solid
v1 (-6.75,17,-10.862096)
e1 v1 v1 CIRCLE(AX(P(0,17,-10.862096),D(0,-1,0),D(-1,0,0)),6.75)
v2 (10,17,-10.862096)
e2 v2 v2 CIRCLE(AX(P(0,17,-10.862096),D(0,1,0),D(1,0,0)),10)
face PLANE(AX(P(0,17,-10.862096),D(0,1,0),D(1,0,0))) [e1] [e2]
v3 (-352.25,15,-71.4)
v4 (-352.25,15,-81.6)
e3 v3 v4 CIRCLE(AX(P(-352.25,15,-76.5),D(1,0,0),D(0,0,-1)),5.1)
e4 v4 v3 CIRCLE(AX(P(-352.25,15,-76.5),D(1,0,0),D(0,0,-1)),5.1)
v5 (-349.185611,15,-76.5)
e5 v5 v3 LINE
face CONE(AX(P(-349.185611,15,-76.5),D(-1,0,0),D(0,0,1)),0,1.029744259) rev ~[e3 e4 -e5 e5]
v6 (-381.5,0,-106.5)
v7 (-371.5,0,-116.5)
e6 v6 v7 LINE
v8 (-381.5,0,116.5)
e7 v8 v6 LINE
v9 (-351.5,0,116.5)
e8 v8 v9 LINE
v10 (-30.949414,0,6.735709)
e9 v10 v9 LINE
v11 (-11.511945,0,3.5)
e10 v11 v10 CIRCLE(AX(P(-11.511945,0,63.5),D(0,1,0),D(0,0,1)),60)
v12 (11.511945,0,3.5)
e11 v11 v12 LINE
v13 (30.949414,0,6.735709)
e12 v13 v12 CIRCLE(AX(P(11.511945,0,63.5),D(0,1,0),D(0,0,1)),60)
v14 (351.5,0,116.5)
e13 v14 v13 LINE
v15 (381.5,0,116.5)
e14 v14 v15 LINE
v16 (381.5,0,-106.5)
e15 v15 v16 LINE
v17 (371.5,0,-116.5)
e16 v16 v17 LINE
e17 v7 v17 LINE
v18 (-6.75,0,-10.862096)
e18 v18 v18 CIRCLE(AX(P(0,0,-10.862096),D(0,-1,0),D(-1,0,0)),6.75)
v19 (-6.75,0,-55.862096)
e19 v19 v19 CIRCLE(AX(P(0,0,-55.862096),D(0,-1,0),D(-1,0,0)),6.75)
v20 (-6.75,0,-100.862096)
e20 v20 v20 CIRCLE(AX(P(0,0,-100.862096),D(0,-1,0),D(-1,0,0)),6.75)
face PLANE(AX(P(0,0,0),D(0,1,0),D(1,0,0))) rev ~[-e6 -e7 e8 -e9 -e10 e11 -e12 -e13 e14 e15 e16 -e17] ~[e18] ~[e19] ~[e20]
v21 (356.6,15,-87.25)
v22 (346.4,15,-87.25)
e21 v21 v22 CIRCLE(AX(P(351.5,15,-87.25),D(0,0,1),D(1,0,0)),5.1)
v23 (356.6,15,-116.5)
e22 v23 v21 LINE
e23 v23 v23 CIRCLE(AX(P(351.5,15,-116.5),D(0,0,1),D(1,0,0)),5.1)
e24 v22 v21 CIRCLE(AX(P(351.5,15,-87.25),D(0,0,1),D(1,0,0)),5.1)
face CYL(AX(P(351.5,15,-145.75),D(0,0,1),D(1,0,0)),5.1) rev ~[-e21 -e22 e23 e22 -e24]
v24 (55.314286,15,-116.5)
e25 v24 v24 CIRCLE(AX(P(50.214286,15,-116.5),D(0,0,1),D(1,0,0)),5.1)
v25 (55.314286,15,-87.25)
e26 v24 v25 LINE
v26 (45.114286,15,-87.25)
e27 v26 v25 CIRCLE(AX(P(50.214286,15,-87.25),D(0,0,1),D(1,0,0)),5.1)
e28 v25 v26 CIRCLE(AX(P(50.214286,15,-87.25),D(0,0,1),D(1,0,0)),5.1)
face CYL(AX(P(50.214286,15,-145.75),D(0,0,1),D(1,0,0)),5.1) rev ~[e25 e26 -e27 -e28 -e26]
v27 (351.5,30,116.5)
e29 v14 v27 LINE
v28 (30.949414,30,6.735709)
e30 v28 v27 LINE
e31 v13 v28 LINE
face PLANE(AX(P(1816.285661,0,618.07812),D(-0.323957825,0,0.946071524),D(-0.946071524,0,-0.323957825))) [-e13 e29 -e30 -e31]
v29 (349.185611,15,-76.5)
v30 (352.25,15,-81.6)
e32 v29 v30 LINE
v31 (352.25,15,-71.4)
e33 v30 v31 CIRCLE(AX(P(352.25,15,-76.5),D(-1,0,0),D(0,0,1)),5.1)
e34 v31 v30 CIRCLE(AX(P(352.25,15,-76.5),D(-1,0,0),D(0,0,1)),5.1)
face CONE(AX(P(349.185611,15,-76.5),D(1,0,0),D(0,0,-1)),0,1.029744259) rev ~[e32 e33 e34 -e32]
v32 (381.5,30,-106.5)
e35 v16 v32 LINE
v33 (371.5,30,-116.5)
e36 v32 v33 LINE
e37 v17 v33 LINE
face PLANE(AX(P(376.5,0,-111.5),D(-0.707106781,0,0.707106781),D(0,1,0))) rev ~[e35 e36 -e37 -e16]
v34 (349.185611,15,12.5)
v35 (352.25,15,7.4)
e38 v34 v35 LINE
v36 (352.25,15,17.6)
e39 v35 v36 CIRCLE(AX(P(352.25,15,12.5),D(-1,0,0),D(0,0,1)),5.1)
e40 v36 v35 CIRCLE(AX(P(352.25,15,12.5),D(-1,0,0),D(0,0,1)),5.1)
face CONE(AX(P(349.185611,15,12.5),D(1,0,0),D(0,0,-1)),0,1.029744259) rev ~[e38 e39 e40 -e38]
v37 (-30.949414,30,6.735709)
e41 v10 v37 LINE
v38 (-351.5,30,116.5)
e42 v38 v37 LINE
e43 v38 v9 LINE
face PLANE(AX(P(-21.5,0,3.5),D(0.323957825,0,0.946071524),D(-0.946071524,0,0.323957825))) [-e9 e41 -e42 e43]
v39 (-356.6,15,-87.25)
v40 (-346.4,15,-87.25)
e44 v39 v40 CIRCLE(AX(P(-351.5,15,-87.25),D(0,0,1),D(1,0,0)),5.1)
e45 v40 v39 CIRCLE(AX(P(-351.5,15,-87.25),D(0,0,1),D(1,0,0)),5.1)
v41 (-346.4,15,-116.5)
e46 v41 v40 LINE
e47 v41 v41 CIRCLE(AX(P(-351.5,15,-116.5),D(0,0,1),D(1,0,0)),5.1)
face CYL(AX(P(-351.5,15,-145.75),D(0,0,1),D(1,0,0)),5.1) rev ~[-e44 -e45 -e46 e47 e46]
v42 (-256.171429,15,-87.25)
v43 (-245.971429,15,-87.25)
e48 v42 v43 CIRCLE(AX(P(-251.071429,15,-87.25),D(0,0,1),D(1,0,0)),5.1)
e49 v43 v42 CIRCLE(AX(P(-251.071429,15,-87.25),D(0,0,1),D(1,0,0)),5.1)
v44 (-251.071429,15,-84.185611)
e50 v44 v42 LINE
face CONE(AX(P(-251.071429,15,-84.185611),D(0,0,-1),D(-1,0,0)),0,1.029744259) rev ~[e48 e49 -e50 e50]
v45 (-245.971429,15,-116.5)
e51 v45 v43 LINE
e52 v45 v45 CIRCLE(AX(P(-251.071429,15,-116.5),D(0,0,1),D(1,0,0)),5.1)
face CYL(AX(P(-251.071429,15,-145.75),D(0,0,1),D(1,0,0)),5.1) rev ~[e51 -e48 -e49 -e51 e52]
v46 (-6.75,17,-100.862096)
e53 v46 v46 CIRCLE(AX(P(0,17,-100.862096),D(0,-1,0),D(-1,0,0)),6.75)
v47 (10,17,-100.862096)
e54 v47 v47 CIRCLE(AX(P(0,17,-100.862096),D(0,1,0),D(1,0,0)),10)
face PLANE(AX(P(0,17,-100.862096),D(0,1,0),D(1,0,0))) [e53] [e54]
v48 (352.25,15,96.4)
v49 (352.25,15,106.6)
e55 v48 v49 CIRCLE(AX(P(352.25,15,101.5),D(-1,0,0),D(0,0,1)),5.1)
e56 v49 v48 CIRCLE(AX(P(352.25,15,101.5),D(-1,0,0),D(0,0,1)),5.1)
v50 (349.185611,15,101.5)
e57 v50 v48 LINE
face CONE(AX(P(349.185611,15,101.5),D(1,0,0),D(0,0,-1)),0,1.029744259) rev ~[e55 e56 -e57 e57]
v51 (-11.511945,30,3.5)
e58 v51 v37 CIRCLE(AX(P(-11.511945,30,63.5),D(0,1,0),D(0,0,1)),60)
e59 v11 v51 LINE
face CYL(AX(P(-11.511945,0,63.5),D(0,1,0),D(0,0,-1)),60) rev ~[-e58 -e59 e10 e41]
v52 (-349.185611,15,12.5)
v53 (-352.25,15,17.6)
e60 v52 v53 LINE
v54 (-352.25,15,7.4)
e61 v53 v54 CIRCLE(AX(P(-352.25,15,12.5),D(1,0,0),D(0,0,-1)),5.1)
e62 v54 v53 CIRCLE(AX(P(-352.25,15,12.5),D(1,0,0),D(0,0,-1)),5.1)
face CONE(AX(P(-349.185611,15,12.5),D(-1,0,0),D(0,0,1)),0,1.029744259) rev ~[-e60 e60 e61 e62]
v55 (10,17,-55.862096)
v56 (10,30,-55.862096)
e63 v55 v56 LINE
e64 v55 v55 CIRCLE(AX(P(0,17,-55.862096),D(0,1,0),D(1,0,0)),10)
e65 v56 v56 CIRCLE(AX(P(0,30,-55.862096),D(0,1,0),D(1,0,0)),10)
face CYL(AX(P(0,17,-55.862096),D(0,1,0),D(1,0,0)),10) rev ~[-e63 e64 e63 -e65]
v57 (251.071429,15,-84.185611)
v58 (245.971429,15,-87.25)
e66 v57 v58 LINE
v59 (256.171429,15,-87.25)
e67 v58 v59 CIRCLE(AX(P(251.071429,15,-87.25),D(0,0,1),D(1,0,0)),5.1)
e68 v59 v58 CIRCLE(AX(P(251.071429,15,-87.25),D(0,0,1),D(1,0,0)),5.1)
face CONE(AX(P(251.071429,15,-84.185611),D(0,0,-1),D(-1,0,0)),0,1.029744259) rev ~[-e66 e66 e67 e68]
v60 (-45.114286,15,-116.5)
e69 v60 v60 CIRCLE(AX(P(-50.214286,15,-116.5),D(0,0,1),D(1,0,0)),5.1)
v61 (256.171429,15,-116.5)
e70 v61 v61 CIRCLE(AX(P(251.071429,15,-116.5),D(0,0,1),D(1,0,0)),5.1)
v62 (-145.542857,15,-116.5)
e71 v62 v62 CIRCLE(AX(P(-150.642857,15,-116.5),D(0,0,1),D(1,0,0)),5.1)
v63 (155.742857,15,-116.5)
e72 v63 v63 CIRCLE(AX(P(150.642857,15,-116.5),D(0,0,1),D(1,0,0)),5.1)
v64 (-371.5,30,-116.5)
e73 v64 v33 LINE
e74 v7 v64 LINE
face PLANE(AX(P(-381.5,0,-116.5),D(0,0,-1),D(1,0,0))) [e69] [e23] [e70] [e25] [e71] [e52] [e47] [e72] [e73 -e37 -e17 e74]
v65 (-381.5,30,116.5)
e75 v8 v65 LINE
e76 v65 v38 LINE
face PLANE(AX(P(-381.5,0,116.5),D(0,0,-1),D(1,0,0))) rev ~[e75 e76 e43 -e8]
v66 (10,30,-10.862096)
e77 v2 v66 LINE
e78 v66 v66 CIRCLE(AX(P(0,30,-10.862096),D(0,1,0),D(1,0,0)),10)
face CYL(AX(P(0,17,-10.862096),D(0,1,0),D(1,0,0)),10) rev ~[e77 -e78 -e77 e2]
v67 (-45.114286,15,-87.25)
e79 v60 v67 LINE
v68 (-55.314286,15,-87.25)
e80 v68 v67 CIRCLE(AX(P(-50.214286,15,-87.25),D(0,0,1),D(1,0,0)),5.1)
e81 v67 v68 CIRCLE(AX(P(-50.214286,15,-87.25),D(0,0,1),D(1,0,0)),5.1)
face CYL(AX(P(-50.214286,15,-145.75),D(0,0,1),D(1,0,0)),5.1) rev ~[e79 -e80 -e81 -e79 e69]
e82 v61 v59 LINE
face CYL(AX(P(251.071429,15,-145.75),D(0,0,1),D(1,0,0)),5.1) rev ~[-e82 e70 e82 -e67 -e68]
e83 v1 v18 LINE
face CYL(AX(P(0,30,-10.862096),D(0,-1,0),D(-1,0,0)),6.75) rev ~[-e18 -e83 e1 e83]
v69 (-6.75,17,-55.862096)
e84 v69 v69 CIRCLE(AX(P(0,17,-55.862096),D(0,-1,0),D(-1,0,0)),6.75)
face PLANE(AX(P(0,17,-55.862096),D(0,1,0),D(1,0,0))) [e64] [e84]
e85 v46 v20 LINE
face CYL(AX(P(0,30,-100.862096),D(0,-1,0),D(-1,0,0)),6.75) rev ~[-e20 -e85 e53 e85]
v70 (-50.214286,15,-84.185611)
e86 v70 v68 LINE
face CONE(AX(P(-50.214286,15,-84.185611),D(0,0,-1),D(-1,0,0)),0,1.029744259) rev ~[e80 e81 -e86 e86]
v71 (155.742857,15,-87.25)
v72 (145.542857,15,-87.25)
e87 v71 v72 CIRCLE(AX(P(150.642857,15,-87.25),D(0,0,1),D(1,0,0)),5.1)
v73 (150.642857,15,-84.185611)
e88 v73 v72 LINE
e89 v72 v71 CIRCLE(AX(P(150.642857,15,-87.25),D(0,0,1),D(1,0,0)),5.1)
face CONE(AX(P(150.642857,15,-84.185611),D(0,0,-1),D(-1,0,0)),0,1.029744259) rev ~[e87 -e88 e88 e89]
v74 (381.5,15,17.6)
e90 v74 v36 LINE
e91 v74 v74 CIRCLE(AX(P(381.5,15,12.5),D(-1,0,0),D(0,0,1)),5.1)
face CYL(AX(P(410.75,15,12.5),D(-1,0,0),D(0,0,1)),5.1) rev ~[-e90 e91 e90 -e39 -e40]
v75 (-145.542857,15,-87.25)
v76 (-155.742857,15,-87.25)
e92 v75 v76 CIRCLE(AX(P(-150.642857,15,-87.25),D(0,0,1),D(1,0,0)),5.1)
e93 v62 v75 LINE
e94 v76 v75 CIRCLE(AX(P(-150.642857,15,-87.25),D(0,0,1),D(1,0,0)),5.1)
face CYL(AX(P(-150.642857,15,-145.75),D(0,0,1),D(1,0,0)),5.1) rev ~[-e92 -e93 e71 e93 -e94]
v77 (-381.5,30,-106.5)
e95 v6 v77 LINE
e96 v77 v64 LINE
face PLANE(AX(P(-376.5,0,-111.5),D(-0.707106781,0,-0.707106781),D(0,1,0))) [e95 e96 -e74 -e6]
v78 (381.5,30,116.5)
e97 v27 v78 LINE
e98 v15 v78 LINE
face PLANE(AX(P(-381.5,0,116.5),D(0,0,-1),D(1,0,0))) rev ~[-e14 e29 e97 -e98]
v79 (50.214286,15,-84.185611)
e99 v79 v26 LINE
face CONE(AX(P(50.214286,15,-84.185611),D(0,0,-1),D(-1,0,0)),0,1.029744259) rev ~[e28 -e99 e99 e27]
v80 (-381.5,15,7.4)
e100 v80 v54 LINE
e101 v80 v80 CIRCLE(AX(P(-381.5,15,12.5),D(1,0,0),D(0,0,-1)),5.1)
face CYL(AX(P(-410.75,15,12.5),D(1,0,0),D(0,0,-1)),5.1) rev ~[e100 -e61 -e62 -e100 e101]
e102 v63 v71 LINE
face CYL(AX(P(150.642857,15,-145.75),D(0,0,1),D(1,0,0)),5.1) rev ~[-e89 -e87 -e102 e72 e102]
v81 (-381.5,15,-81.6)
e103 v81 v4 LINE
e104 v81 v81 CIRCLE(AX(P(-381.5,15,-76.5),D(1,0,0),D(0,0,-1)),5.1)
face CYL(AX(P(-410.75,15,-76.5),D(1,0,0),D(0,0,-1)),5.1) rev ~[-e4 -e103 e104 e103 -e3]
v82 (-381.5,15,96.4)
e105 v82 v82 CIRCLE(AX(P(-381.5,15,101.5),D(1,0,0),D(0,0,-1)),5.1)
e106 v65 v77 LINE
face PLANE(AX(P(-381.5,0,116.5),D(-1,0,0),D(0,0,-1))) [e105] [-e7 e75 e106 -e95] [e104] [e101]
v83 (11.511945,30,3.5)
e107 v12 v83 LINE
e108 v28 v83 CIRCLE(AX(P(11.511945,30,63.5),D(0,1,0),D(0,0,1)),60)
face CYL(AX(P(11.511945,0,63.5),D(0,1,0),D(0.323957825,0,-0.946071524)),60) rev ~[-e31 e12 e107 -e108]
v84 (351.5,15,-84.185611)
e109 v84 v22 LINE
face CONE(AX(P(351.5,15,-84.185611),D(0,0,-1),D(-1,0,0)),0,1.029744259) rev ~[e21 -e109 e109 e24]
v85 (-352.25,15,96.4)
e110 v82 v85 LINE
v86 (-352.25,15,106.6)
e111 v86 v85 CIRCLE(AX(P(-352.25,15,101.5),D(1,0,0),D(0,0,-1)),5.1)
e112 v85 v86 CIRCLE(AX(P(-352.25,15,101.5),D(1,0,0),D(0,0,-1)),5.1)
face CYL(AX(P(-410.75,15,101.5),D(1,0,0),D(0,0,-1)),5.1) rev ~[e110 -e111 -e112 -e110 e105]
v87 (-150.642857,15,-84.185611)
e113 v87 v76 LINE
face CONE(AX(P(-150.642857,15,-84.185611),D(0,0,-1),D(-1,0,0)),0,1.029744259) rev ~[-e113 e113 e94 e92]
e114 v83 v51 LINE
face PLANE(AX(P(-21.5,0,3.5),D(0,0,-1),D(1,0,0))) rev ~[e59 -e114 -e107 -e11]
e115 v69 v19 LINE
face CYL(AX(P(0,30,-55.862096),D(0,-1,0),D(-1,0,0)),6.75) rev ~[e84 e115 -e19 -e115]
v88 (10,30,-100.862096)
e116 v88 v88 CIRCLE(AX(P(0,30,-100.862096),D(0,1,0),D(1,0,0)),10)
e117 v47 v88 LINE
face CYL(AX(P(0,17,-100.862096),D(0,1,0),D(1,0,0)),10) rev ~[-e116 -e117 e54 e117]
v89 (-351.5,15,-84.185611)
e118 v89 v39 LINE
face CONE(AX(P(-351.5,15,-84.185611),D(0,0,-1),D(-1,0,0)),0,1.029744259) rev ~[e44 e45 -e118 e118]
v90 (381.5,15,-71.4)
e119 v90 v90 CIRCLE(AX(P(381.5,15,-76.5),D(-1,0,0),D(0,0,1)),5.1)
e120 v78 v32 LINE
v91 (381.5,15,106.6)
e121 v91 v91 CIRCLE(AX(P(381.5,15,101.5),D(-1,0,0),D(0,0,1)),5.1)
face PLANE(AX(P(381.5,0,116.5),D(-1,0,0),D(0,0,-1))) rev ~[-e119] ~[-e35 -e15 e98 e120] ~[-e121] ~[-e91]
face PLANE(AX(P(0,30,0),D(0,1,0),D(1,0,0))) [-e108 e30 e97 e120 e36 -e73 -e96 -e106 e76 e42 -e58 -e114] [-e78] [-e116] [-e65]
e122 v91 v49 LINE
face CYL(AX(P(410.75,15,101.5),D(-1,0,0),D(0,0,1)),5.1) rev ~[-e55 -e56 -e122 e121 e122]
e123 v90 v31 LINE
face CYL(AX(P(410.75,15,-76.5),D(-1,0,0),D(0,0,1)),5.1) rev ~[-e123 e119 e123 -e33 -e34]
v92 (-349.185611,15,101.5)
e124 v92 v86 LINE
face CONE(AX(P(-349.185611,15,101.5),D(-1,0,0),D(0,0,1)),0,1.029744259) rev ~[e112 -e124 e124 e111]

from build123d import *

# Parameters (mm, degrees)
SKETCH_1_W                = 763
SKETCH_1_H                = 233
EXTRUDE_1_DEPTH           = 30
CHAMFER_1_SIZE            = 10
CUT_EXTRUDE_1_DEPTH       = 401.018124589
CUT_EXTRUDE_1_DEPTH_BACK  = 30
FILLET_1_R                = 60
HOLE_WIZARD_1_D           = 13.5
HOLE_WIZARD_1_CBORE_D     = 20
HOLE_WIZARD_1_CBORE_DEPTH = 13
HOLE_WIZARD_M12_1_D       = 10.2
HOLE_WIZARD_M12_1_DEPTH   = 29.25
HOLE_WIZARD_M12_1_TIP     = 3.064389157
HOLE_WIZARD_M12_2_D       = 10.2
HOLE_WIZARD_M12_2_DEPTH   = 29.25
HOLE_WIZARD_M12_2_TIP     = 3.064389157
HOLE_WIZARD_M12_3_D       = 10.2
HOLE_WIZARD_M12_3_DEPTH   = 29.25
HOLE_WIZARD_M12_3_TIP     = 3.064389157


with BuildPart() as part:
    # 草图1 → 凸台-拉伸1 (new body)
    with BuildSketch(Plane(origin=(0, 0, 0), x_dir=(1, 0, 0), z_dir=(0, 1, 0))):
        Rectangle(SKETCH_1_W, SKETCH_1_H)
    extrude(amount=EXTRUDE_1_DEPTH)

    # 倒角1
    chamfer_1_edges = [part.edges().sort_by_distance(p)[0] for p in [
        (-381.5, 15, -116.5),
        (381.5, 15, -116.5),
    ]]
    chamfer(chamfer_1_edges, length=CHAMFER_1_SIZE)

    # 草图2 → 切除-拉伸1 (cut, two sides: drawn at the far end of the back side and taken through both)
    with BuildSketch(Plane(origin=(0, 30, 0), x_dir=(1, 0, 0), z_dir=(0, 1, 0)).offset(-CUT_EXTRUDE_1_DEPTH_BACK)):
        Polygon((-1816.285660926, -618.078120257), (-351.5, -116.5), (-21.5, -3.5), (21.5, -3.5), (351.5, -116.5), (1816.285660926, -618.078120257), (1816.285660926, -3714.642437803), (-1816.285660926, -3714.642437803), align=None)
    extrude(amount=CUT_EXTRUDE_1_DEPTH + CUT_EXTRUDE_1_DEPTH_BACK, mode=Mode.SUBTRACT)

    # 圆角1
    fillet_1_edges = [part.edges().sort_by_distance(p)[0] for p in [
        (21.5, 15, 3.5),
        (-21.5, 15, 3.5),
    ]]
    fillet(fillet_1_edges, radius=FILLET_1_R)

    # 打孔尺寸(%根据)内六角圆柱头螺钉的类型1 (through all)
    with Locations(Plane(origin=(0, 30, 0), x_dir=(1, 0, 0), z_dir=(0, 1, 0))):
        with Locations((0, 100.862096352), (0, 55.862096352), (0, 10.862096352)):
            CounterBoreHole(HOLE_WIZARD_1_D / 2, HOLE_WIZARD_1_CBORE_D / 2, HOLE_WIZARD_1_CBORE_DEPTH)

    # M12 螺纹孔1
    with Locations(Plane(origin=(0, 0, -116.5), x_dir=(-1, 0, 0), z_dir=(0, 0, -1))):
        with Locations((351.5, 15), (251.071428571, 15), (150.642857143, 15), (50.214285714, 15), (-50.214285714, 15), (-150.642857143, 15), (-251.071428571, 15), (-351.5, 15)):
            Hole(HOLE_WIZARD_M12_1_D / 2, depth=HOLE_WIZARD_M12_1_DEPTH)
            with Locations((0, 0, -(HOLE_WIZARD_M12_1_DEPTH + HOLE_WIZARD_M12_1_TIP / 2))):  # 118° drill point
                Cone(0, HOLE_WIZARD_M12_1_D / 2, HOLE_WIZARD_M12_1_TIP, mode=Mode.SUBTRACT)

    # M12 螺纹孔2
    with Locations(Plane(origin=(381.5, 0, 0), x_dir=(0, 0, -1), z_dir=(1, 0, 0))):
        with Locations((76.5, 15), (-12.5, 15), (-101.5, 15)):
            Hole(HOLE_WIZARD_M12_2_D / 2, depth=HOLE_WIZARD_M12_2_DEPTH)
            with Locations((0, 0, -(HOLE_WIZARD_M12_2_DEPTH + HOLE_WIZARD_M12_2_TIP / 2))):  # 118° drill point
                Cone(0, HOLE_WIZARD_M12_2_D / 2, HOLE_WIZARD_M12_2_TIP, mode=Mode.SUBTRACT)

    # M12 螺纹孔3
    with Locations(Plane.ZY.offset(381.5)):
        with Locations((-76.5, 15), (12.5, 15), (101.5, 15)):
            Hole(HOLE_WIZARD_M12_3_D / 2, depth=HOLE_WIZARD_M12_3_DEPTH)
            with Locations((0, 0, -(HOLE_WIZARD_M12_3_DEPTH + HOLE_WIZARD_M12_3_TIP / 2))):  # 118° drill point
                Cone(0, HOLE_WIZARD_M12_3_D / 2, HOLE_WIZARD_M12_3_TIP, mode=Mode.SUBTRACT)


solid = part.part
